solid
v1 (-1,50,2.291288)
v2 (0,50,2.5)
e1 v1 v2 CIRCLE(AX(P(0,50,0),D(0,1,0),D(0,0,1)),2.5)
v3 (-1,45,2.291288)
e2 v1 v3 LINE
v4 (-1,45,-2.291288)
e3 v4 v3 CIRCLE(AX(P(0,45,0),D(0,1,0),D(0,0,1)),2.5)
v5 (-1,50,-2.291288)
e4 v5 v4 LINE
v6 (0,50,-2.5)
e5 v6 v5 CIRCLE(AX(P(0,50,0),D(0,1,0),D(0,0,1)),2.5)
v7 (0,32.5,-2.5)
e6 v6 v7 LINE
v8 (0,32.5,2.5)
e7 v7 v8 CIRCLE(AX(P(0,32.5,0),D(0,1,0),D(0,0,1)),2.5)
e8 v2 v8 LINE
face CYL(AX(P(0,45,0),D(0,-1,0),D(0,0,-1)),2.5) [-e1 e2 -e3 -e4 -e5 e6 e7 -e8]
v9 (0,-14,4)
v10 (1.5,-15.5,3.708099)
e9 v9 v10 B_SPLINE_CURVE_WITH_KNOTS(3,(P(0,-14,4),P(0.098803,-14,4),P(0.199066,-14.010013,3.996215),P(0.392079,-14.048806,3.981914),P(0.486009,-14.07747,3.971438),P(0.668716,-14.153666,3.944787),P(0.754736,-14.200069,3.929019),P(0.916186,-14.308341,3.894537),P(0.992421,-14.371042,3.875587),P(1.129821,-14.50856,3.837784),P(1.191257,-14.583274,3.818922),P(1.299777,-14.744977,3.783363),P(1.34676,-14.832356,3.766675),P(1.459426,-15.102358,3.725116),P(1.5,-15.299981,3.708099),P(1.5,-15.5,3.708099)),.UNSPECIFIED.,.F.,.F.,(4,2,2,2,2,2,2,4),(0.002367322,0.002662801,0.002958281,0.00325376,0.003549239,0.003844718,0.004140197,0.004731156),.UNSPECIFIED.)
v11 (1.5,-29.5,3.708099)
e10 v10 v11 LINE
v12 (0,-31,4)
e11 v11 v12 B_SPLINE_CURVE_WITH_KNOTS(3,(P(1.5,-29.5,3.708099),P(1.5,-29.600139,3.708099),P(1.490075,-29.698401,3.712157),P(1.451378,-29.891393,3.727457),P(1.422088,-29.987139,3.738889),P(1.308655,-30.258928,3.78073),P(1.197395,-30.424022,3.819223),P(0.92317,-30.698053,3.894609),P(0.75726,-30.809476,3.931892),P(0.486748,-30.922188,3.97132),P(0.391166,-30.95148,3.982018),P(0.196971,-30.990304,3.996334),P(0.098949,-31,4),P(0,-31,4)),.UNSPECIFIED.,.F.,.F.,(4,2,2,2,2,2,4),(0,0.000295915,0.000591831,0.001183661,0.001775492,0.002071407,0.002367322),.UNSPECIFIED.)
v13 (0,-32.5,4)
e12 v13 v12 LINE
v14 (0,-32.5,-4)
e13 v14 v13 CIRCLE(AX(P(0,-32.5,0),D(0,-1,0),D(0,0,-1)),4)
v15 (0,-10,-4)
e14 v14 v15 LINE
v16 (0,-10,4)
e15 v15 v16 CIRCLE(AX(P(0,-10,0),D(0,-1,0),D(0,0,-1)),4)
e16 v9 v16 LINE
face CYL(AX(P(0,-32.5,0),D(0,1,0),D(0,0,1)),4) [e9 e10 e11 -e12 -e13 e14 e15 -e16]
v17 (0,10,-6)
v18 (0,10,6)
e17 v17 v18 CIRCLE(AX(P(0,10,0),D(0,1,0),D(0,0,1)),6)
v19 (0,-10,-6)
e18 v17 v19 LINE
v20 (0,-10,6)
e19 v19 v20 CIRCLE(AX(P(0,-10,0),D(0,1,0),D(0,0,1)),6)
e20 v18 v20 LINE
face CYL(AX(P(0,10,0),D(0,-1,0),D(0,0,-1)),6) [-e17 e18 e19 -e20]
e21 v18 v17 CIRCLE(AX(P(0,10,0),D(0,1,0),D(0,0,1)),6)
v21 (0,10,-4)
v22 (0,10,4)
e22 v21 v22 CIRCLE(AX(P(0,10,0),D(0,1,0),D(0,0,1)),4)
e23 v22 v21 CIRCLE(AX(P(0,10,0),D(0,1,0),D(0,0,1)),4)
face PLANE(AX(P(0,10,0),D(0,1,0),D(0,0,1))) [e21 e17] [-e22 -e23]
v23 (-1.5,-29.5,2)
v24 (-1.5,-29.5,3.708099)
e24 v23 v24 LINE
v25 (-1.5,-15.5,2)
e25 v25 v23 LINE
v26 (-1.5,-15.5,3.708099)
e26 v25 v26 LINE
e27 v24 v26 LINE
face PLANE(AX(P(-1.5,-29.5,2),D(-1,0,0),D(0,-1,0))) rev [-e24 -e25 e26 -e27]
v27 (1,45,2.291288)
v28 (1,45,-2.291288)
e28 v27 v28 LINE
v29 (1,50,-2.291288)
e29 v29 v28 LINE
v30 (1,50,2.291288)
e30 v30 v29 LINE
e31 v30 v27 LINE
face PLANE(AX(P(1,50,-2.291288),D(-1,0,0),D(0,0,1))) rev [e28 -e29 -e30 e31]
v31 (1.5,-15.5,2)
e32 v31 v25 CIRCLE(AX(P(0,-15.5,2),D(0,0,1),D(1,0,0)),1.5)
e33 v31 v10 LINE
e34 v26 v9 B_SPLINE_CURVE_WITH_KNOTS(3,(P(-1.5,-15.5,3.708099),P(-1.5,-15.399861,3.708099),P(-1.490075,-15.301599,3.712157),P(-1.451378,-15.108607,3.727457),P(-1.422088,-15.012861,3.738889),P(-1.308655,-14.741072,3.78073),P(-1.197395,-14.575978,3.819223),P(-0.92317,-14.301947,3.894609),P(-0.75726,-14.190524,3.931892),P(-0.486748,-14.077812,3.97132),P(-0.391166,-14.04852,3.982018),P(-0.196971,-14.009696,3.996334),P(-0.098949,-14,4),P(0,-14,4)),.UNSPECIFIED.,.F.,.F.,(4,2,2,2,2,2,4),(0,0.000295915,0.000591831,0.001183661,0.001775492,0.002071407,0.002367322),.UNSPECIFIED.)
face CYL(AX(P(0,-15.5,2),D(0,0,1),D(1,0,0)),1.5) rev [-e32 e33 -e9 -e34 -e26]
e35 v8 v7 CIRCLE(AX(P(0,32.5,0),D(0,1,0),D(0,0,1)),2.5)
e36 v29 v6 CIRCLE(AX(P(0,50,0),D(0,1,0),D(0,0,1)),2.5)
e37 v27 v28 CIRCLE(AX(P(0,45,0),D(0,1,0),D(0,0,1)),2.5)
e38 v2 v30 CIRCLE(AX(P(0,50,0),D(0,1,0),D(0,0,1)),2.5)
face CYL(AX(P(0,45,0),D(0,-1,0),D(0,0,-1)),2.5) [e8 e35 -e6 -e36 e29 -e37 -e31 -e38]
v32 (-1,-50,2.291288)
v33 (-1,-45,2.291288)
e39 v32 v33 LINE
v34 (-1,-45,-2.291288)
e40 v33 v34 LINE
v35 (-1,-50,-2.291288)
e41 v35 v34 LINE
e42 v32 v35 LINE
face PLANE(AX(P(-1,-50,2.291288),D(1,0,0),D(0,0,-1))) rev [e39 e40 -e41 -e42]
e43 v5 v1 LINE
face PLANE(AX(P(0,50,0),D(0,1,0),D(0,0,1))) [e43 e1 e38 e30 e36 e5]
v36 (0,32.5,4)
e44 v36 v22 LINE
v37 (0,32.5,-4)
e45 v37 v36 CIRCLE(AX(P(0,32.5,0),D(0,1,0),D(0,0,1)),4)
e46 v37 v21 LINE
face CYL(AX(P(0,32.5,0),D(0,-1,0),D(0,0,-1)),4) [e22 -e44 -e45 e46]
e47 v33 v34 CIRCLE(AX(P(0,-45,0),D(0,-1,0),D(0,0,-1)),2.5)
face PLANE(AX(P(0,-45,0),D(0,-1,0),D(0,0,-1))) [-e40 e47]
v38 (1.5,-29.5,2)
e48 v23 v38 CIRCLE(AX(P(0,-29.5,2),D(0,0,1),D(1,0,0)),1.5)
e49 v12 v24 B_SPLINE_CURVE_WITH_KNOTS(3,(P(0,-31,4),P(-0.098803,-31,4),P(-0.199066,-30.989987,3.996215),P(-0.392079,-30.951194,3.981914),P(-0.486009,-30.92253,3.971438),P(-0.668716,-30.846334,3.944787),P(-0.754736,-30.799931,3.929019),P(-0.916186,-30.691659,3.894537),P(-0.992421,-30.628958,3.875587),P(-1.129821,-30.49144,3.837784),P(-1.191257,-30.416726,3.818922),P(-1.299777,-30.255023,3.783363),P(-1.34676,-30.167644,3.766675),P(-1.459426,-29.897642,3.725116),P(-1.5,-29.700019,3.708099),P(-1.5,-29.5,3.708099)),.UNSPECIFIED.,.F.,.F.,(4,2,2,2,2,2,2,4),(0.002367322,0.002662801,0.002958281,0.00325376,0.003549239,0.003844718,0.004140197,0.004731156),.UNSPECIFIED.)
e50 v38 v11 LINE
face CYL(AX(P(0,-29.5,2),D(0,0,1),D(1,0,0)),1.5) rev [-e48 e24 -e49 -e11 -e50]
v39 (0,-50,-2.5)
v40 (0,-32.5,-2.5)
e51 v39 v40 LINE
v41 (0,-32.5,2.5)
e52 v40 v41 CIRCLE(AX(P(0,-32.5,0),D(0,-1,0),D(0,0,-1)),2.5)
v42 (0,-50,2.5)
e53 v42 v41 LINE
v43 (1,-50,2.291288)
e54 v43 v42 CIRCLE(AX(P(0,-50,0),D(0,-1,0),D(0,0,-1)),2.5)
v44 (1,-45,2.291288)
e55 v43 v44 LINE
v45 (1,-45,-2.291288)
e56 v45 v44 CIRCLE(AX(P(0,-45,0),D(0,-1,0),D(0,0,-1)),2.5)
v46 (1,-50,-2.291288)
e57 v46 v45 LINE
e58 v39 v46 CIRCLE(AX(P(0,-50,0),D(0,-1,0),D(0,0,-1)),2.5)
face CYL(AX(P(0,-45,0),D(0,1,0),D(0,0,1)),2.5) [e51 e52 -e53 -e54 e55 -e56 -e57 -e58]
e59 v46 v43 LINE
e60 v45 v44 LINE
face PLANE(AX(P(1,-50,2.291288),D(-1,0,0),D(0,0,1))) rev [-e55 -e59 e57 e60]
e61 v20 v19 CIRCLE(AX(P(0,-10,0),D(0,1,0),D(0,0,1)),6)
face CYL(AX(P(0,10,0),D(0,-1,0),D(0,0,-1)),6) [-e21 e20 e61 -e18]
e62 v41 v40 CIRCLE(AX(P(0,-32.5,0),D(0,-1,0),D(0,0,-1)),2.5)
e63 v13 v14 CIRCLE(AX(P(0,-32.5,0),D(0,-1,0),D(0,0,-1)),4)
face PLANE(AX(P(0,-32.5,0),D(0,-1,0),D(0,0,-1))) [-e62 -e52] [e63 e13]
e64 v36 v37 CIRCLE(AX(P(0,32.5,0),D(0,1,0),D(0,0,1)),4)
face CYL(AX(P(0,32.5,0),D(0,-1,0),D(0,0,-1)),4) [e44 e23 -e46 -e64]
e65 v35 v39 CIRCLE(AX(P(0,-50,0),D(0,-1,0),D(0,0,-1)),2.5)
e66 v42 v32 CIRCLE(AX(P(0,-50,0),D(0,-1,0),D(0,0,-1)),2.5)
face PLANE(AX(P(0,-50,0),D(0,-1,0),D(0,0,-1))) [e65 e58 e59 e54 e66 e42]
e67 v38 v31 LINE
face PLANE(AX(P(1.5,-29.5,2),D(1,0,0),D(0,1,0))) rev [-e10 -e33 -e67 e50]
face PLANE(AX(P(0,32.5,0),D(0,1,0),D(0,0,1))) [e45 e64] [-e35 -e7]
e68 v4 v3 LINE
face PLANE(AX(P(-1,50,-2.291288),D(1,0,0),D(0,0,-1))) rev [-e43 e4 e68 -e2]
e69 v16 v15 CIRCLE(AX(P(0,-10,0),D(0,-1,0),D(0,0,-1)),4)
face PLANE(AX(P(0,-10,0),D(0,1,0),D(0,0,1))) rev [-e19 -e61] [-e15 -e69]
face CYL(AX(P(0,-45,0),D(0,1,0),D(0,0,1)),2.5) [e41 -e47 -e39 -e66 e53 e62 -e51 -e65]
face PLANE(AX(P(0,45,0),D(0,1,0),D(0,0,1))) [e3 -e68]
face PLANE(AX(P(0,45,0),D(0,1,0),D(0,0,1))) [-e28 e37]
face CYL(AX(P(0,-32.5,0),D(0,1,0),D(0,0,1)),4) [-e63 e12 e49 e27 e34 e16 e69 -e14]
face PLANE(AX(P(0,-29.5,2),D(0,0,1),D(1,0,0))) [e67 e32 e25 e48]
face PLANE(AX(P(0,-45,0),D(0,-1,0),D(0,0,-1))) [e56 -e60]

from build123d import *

# Parameters (mm, degrees)
SKETCH1_R           = 6
BOSS_EXTRUDE1_DEPTH = 10
SKETCH2_R           = 4
BOSS_EXTRUDE2_DEPTH = 22.5
SKETCH3_R           = 2.5
BOSS_EXTRUDE3_DEPTH = 12.5
BOSS_EXTRUDE4_START = 22.5
SKETCH4_R           = 4
BOSS_EXTRUDE4_DEPTH = 22.5
BOSS_EXTRUDE5_START = 12.5
SKETCH5_R           = 2.5
BOSS_EXTRUDE5_DEPTH = 12.5
BOSS_EXTRUDE6_START = 5
BOSS_EXTRUDE6_DEPTH = 5
BOSS_EXTRUDE7_DEPTH = 5
CUT_EXTRUDE1_DEPTH  = 2


with BuildPart() as part:
    # Sketch1 → Boss-Extrude1 (new, symmetric)
    with BuildSketch(Plane(origin=(0, 0, 0), x_dir=(1, 0, 0), z_dir=(0, 1, 0))):
        with Locations(Location((0, 0, 0), (0, 0, 270))):
            Circle(SKETCH1_R)
    extrude(amount=BOSS_EXTRUDE1_DEPTH, both=True)

    # Sketch2 → Boss-Extrude2 (add)
    with BuildSketch(Plane(origin=(0, 10, 0), x_dir=(1, 0, 0), z_dir=(0, 1, 0))):
        with Locations(Location((0, 0, 0), (0, 0, 90))):
            Circle(SKETCH2_R)
    extrude(amount=BOSS_EXTRUDE2_DEPTH)

    # Sketch3 → Boss-Extrude3 (add)
    with BuildSketch(Plane(origin=(0, 32.5, 0), x_dir=(1, 0, 0), z_dir=(0, 1, 0))):
        with Locations(Location((0, 0, 0), (0, 0, 270))):
            Circle(SKETCH3_R)
    extrude(amount=BOSS_EXTRUDE3_DEPTH)

    # Sketch4 → Boss-Extrude4 (add)
    with BuildSketch(Plane.XZ.offset(10).offset(BOSS_EXTRUDE4_START)):
        with Locations(Location((0, 0, 0), (0, 0, 270))):
            Circle(SKETCH4_R)
    extrude(amount=-BOSS_EXTRUDE4_DEPTH)

    # Sketch5 → Boss-Extrude5 (add)
    with BuildSketch(Plane.XZ.offset(32.5).offset(BOSS_EXTRUDE5_START)):
        with Locations(Location((0, 0, 0), (0, 0, 90))):
            Circle(SKETCH5_R)
    extrude(amount=-BOSS_EXTRUDE5_DEPTH)

    # Sketch6 → Boss-Extrude6 (add)
    with BuildSketch(Plane(origin=(0, -45, 0), x_dir=(-1, 0, 0), z_dir=(0, -1, 0)).offset(BOSS_EXTRUDE6_START)):
        with BuildLine():
            Line((1, -2.291287847), (1, 2.291287847))
            ThreePointArc((1, 2.291287847), (0, 2.5), (-1, 2.291287847))
            Line((-1, 2.291287847), (-1, -2.291287847))
            ThreePointArc((-1, -2.291287847), (0, -2.5), (1, -2.291287847))
        make_face()
    extrude(amount=-BOSS_EXTRUDE6_DEPTH)

    # Sketch7 → Boss-Extrude7 (add)
    with BuildSketch(Plane(origin=(0, 45, 0), x_dir=(1, 0, 0), z_dir=(0, 1, 0))):
        with BuildLine():
            Line((-1, 2.291287847), (-1, -2.291287847))
            ThreePointArc((-1, -2.291287847), (0, -2.5), (1, -2.291287847))
            Line((1, -2.291287847), (1, 2.291287847))
            ThreePointArc((1, 2.291287847), (0, 2.5), (-1, 2.291287847))
        make_face()
    extrude(amount=BOSS_EXTRUDE7_DEPTH)

    # Sketch8 → Cut-Extrude1 (cut)
    with BuildSketch(Plane.XY.offset(4)):
        with BuildLine():
            Line((-1.5, -29.5), (-1.5, -15.5))
            ThreePointArc((-1.5, -15.5), (0, -14), (1.5, -15.5))
            Line((1.5, -15.5), (1.5, -29.5))
            ThreePointArc((1.5, -29.5), (0, -31), (-1.5, -29.5))
        make_face()
    extrude(amount=-CUT_EXTRUDE1_DEPTH, mode=Mode.SUBTRACT)


solid = part.part
